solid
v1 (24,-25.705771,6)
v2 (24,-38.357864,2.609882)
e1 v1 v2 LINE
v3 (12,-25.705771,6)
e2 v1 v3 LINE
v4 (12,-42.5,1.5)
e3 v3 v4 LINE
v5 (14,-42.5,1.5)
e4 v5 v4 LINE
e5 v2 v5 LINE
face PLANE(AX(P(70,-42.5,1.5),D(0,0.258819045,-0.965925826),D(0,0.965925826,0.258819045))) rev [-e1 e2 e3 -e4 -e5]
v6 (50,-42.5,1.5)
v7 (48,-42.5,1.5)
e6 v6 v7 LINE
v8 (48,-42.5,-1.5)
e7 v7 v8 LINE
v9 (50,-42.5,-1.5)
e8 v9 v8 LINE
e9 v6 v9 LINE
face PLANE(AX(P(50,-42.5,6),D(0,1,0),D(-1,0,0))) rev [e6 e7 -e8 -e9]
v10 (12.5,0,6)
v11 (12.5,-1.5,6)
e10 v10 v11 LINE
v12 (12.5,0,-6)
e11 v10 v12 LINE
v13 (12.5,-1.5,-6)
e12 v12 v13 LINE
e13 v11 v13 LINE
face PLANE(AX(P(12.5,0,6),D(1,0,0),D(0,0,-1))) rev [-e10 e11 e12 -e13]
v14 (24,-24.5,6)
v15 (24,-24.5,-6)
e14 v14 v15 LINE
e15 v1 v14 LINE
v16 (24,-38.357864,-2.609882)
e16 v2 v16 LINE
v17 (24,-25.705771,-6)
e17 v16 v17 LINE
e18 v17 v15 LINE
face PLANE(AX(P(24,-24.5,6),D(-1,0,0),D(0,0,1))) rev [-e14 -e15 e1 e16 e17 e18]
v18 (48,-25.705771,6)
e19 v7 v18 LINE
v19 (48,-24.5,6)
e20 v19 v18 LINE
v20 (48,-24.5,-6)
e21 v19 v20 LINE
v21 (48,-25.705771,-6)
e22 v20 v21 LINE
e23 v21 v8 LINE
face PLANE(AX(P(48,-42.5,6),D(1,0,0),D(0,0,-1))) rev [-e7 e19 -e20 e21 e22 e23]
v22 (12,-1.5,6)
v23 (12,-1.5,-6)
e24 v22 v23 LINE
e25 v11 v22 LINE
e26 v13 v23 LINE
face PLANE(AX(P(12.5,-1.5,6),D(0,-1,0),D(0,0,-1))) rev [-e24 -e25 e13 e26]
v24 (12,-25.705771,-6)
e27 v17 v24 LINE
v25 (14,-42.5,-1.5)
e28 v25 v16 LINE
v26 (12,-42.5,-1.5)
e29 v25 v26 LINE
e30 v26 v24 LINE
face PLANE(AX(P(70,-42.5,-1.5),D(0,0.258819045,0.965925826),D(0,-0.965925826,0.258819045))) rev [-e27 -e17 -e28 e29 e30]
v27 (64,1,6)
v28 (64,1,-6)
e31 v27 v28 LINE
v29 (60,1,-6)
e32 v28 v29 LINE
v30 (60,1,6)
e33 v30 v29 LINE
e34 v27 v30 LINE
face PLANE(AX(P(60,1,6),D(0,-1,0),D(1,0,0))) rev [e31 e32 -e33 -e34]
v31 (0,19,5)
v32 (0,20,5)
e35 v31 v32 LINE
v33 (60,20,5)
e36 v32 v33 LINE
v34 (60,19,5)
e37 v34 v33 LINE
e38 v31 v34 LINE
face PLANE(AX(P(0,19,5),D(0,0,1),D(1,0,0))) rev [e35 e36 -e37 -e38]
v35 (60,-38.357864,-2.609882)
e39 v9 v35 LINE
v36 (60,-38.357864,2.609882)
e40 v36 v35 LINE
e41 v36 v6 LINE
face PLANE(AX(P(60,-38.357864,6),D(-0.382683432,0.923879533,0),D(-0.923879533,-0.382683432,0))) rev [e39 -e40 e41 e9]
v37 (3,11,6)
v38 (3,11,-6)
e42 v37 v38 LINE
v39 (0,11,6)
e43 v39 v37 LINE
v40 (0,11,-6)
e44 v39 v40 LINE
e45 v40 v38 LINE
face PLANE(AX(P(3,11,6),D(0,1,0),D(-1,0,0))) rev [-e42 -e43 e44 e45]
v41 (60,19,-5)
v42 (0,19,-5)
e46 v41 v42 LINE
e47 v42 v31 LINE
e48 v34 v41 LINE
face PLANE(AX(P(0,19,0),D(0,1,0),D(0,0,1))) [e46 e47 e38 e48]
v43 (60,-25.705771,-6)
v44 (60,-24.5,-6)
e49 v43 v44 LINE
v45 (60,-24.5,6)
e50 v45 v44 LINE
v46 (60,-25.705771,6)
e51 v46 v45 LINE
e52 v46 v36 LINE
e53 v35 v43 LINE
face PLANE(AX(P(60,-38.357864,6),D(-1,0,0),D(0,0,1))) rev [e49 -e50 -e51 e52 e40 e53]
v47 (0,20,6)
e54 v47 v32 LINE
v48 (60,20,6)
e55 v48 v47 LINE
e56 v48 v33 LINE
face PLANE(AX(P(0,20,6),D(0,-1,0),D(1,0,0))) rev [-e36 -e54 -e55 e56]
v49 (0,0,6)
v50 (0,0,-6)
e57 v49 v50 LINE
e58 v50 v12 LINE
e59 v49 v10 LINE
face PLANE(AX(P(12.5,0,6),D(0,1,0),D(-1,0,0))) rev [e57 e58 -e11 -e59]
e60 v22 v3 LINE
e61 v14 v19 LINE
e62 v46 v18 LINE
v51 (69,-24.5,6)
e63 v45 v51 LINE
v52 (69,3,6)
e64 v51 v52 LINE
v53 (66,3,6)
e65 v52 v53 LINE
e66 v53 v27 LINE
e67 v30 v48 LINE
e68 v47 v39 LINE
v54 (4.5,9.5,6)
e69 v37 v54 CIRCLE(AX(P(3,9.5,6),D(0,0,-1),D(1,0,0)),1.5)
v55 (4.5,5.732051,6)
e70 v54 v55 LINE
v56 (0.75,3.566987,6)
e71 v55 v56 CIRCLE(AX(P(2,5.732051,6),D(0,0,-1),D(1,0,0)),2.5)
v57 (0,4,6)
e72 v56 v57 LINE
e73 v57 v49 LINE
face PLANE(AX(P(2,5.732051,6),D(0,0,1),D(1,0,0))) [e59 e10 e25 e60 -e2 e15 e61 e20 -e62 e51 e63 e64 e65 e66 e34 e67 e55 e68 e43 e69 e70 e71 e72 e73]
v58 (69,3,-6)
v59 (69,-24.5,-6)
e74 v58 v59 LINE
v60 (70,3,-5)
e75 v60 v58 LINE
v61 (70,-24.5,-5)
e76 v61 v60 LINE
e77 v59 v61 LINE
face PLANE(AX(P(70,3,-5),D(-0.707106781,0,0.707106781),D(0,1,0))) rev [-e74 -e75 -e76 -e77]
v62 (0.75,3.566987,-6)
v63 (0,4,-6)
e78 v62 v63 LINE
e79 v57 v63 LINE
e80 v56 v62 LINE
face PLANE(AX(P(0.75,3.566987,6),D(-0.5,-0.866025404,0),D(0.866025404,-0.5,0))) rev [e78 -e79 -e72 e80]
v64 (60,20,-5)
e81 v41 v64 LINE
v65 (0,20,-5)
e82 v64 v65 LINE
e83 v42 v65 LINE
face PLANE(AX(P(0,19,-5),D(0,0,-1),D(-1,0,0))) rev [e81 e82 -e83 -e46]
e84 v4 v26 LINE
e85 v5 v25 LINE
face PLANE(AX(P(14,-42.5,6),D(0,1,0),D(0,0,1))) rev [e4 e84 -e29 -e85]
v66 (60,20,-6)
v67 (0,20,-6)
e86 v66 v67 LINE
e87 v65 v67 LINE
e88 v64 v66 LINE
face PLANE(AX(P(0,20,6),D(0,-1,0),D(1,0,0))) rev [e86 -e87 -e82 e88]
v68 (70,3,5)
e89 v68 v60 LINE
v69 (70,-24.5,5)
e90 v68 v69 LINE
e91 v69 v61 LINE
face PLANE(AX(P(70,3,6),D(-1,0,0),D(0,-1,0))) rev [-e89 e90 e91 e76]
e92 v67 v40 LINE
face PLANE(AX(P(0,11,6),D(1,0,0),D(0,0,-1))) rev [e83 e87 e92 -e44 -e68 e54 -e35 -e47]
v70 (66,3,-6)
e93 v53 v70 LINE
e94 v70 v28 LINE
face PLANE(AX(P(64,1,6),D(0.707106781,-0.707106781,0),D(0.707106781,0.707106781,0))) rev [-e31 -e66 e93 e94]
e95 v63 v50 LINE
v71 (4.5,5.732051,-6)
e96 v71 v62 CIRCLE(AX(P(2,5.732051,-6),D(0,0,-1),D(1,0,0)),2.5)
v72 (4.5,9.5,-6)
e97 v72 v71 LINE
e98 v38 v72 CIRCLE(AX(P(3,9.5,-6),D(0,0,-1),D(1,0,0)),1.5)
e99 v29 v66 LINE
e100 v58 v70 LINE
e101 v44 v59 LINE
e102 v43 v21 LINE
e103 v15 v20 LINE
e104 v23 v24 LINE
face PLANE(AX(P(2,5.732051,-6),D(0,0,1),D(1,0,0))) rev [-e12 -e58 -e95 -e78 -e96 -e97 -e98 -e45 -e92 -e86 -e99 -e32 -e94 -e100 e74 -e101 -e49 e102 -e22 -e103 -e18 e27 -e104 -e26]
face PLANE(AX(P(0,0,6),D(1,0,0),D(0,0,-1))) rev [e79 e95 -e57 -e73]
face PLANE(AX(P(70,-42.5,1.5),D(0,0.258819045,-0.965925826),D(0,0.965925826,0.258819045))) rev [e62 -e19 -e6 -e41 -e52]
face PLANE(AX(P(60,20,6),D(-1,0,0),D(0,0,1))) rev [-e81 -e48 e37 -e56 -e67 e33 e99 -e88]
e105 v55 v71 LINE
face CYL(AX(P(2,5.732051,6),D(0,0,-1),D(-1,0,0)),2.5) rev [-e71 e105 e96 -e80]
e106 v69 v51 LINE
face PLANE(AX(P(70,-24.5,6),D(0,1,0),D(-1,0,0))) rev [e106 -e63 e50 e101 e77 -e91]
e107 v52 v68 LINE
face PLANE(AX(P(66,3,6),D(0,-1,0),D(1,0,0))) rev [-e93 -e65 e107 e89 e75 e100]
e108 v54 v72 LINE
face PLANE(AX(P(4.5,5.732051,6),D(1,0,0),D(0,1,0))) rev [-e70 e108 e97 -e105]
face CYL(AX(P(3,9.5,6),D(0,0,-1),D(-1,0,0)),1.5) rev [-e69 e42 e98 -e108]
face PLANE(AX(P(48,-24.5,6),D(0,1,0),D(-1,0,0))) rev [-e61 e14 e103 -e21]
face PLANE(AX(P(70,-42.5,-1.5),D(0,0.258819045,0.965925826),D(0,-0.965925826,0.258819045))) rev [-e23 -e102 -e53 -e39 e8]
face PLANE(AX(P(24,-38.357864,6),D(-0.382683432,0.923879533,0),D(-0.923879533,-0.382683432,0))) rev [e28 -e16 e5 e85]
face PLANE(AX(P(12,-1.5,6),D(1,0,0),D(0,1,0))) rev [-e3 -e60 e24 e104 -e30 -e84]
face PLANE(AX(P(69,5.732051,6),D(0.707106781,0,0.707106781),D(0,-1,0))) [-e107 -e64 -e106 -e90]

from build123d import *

# Parameters (mm, degrees)
EXTRUDE_1_DEPTH     = 6
CUT_EXTRUDE_1_DEPTH = 73.154348448
SKETCH_5_W          = 60
SKETCH_5_H          = 10
CUT_EXTRUDE_2_DEPTH = 1
CHAMFER_1_SIZE      = 1


with BuildPart() as part:
    # 草图1 → 凸台-拉伸1 (new, symmetric)
    with BuildSketch(Plane.XY):
        with BuildLine():
            Line((0, 0), (0, 4))
            Line((0, 4), (0.75, 3.566987298))
            ThreePointArc((0.75, 3.566987298), (3.25, 3.566987298), (4.5, 5.732050808))
            Line((4.5, 5.732050808), (4.5, 9.5))
            ThreePointArc((4.5, 9.5), (4.060660172, 10.560660172), (3, 11))
            Line((3, 11), (0, 11))
            Line((0, 11), (0, 20))
            Line((0, 20), (60, 20))
            Line((60, 20), (60, 1))
            Line((60, 1), (64, 1))
            Line((64, 1), (66, 3))
            Line((66, 3), (70, 3))
            Line((70, 3), (70, -24.5))
            Line((70, -24.5), (60, -24.5))
            Line((60, -24.5), (60, -38.357864376))
            Line((60, -38.357864376), (50, -42.5))
            Line((50, -42.5), (48, -42.5))
            Line((48, -42.5), (48, -24.5))
            Line((48, -24.5), (24, -24.5))
            Line((24, -24.5), (24, -38.357864376))
            Line((24, -38.357864376), (14, -42.5))
            Line((14, -42.5), (12, -42.5))
            Line((12, -42.5), (12, -1.5))
            Line((12, -1.5), (12.5, -1.5))
            Line((12.5, -1.5), (12.5, 0))
            Line((12.5, 0), (0, 0))
        make_face()
    extrude(amount=EXTRUDE_1_DEPTH, both=True)

    # 草图2 → 切除-拉伸1 (cut, through all)
    with BuildSketch(Plane.ZY.offset(-12)):
        Polygon((6, -25.705771366), (6, -47.5), (-6, -47.5), (-6, -25.705771366), (-1.5, -42.5), (1.5, -42.5), align=None)
    extrude(amount=-CUT_EXTRUDE_1_DEPTH, mode=Mode.SUBTRACT)

    # 草图5 → 切除-拉伸2 (cut)
    with BuildSketch(Plane(origin=(0, 20, 0), x_dir=(1, 0, 0), z_dir=(0, 1, 0))):
        with Locations((30, 0)):
            Rectangle(SKETCH_5_W, SKETCH_5_H)
    extrude(amount=-CUT_EXTRUDE_2_DEPTH, mode=Mode.SUBTRACT)

    # 倒角1
    chamfer_1_edges = [part.edges().sort_by_distance(p)[0] for p in [
        (70, -10.75, -6),
        (70, -10.75, 6),
    ]]
    chamfer(chamfer_1_edges, length=CHAMFER_1_SIZE)


solid = part.part
